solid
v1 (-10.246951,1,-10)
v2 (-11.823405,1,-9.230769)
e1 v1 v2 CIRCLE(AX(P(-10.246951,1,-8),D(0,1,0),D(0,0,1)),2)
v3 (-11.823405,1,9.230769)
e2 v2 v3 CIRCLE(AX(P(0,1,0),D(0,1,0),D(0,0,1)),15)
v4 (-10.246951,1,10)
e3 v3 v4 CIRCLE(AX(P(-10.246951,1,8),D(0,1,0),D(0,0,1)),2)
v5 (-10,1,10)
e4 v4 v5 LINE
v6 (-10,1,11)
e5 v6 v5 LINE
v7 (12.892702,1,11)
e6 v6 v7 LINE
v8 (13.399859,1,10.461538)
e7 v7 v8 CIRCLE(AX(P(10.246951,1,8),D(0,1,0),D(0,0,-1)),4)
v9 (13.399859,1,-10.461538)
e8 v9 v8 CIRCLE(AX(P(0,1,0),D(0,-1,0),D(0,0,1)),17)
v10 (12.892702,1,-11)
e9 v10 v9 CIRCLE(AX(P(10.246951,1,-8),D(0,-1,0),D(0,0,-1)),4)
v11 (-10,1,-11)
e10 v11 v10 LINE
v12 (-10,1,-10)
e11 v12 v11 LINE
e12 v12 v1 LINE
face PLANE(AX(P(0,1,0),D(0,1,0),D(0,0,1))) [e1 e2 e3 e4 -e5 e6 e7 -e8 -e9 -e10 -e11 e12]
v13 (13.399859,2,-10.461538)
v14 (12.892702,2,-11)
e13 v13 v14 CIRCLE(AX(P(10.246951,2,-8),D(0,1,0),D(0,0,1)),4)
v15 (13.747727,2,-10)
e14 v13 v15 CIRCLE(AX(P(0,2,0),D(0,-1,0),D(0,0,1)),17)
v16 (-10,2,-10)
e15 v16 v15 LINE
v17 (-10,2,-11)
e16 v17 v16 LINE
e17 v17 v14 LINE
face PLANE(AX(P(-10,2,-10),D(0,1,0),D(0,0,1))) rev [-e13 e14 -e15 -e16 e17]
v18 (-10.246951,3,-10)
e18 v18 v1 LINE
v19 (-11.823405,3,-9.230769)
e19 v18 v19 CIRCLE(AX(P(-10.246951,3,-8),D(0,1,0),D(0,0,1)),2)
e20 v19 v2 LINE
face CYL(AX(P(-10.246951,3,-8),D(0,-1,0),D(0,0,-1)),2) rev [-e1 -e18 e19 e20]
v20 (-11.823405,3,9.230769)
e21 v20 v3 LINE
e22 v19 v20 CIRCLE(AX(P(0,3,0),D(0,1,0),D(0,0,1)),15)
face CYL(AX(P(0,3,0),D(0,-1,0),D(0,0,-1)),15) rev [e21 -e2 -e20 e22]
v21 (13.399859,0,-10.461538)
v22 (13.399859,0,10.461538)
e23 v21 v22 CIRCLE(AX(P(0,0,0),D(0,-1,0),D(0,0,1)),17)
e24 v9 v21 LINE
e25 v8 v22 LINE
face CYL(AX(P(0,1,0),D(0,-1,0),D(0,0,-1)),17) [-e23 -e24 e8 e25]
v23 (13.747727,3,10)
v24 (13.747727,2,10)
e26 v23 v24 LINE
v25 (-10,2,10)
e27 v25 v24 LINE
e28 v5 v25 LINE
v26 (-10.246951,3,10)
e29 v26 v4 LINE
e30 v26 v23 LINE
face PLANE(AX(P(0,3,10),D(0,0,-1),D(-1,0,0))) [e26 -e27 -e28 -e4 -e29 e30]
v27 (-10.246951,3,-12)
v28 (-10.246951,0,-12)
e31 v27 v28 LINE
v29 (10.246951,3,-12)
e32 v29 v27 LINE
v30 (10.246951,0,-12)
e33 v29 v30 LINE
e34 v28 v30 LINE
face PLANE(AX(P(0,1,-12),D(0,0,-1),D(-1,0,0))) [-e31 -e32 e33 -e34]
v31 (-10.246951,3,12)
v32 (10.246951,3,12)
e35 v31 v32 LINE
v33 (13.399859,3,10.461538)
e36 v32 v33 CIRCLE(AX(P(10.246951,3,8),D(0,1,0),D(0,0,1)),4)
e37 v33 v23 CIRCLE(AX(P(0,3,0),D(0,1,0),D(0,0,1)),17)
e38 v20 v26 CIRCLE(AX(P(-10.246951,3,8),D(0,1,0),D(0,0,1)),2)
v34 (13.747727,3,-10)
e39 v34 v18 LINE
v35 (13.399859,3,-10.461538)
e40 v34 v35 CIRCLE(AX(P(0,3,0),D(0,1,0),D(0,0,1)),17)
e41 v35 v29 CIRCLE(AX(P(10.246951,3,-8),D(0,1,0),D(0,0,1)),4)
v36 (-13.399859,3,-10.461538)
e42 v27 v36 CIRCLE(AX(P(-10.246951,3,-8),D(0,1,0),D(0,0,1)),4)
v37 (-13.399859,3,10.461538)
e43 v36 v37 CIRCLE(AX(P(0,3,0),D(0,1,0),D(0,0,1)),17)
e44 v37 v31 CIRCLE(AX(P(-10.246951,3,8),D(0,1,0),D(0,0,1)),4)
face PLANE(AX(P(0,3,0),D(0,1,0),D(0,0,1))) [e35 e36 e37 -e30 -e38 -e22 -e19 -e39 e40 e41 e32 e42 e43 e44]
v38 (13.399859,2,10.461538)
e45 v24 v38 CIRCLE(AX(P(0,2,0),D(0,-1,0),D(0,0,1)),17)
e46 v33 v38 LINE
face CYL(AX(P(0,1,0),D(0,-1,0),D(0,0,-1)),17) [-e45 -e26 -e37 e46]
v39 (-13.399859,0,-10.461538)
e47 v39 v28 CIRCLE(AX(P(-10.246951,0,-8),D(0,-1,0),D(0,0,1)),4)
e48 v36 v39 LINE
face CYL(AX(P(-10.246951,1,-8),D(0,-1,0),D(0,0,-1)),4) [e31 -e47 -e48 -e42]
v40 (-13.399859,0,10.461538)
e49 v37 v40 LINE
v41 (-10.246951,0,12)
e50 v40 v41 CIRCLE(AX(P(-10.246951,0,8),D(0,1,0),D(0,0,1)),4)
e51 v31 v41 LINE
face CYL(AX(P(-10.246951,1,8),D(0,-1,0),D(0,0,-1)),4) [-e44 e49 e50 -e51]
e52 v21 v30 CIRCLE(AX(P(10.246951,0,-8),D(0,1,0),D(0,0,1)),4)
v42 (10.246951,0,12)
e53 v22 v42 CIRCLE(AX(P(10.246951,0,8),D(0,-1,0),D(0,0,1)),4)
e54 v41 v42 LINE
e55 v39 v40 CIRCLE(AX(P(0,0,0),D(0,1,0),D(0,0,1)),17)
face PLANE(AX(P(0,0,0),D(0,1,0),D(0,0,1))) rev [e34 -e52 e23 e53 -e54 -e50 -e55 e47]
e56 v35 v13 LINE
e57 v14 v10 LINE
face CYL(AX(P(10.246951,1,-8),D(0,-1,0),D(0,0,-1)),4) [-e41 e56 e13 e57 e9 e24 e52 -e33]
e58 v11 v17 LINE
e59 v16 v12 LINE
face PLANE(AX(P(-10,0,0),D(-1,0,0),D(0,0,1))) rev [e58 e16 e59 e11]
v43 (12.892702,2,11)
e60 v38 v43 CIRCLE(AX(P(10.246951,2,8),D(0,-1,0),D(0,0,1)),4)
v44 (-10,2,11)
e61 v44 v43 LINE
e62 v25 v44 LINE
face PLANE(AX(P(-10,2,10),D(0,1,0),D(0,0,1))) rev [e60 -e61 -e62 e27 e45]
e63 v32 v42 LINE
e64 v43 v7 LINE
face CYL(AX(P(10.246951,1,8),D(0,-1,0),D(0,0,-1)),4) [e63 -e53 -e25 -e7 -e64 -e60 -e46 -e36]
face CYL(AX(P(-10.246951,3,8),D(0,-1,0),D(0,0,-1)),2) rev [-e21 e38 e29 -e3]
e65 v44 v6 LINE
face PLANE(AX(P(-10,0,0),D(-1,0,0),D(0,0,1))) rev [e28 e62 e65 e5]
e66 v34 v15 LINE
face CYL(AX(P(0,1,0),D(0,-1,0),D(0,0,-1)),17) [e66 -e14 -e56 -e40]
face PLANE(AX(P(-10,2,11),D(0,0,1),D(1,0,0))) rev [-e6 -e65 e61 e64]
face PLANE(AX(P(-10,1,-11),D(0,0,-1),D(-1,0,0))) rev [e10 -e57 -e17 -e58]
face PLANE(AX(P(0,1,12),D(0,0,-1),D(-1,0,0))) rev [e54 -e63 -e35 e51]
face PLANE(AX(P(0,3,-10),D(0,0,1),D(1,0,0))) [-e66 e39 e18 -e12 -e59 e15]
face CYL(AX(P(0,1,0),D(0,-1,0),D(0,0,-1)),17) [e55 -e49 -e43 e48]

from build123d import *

# Parameters (mm, degrees)
BASE_PLATE_DEPTH       = 1
RIM_WALL_DEPTH         = 2
SIDE_GROOVE_A_SKETCH_W = 1
SIDE_GROOVE_A_SKETCH_H = 1
SIDE_GROOVE_A_DEPTH    = 40
SIDE_GROOVE_B_SKETCH_W = 1
SIDE_GROOVE_B_SKETCH_H = 1
SIDE_GROOVE_B_DEPTH    = 40


with BuildPart() as part:
    # Base Plate Sketch → Base Plate (new body)
    with BuildSketch(Plane(origin=(0, 0, 0), x_dir=(1, 0, 0), z_dir=(0, 1, 0))):
        with BuildLine():
            Line((-10.246950766, 12), (10.246950766, 12))
            ThreePointArc((10.246950766, 12), (12.001066805, 11.594868137), (13.399858694, 10.461538462))
            ThreePointArc((13.399858694, 10.461538462), (17, 0), (13.399858694, -10.461538462))
            ThreePointArc((13.399858694, -10.461538462), (12.001066805, -11.594868137), (10.246950766, -12))
            Line((10.246950766, -12), (-10.246950766, -12))
            ThreePointArc((-10.246950766, -12), (-12.001066805, -11.594868137), (-13.399858694, -10.461538462))
            ThreePointArc((-13.399858694, -10.461538462), (-17, 0), (-13.399858694, 10.461538462))
            ThreePointArc((-13.399858694, 10.461538462), (-12.001066805, 11.594868137), (-10.246950766, 12))
        make_face()
    extrude(amount=BASE_PLATE_DEPTH)

    # Rim Wall Sketch → Rim Wall (add)
    with BuildSketch(Plane(origin=(0, 1, 0), x_dir=(1, 0, 0), z_dir=(0, 1, 0))):
        with BuildLine():
            Line((10.246950766, -10), (-10.246950766, -10))
            ThreePointArc((-10.246950766, -10), (-11.124008785, -9.797434069), (-11.82340473, -9.230769231))
            ThreePointArc((-11.82340473, -9.230769231), (-15, 0), (-11.82340473, 9.230769231))
            ThreePointArc((-11.82340473, 9.230769231), (-11.124008785, 9.797434069), (-10.246950766, 10))
            Line((-10.246950766, 10), (10.246950766, 10))
            Line((10.246950766, 10), (13.747727085, 10))
            ThreePointArc((13.747727085, 10), (13.575754412, 10.232247659), (13.399858694, 10.461538462))
            ThreePointArc((13.399858694, 10.461538462), (12.001066805, 11.594868137), (10.246950766, 12))
            Line((10.246950766, 12), (-10.246950766, 12))
            ThreePointArc((-10.246950766, 12), (-12.001066805, 11.594868137), (-13.399858694, 10.461538462))
            ThreePointArc((-13.399858694, 10.461538462), (-17, 0), (-13.399858694, -10.461538462))
            ThreePointArc((-13.399858694, -10.461538462), (-12.001066805, -11.594868137), (-10.246950766, -12))
            Line((-10.246950766, -12), (10.246950766, -12))
            ThreePointArc((10.246950766, -12), (12.001066805, -11.594868137), (13.399858694, -10.461538462))
            ThreePointArc((13.399858694, -10.461538462), (13.575754412, -10.232247659), (13.747727085, -10))
            Line((13.747727085, -10), (10.246950766, -10))
        make_face()
    extrude(amount=RIM_WALL_DEPTH)

    # Side Groove A Sketch → Side Groove A (cut)
    with BuildSketch(Plane(origin=(30, 0, 0), x_dir=(0, 0, -1), z_dir=(1, 0, 0))):
        with Locations((-10.5, 1.5)):
            Rectangle(SIDE_GROOVE_A_SKETCH_W, SIDE_GROOVE_A_SKETCH_H)
    extrude(amount=-SIDE_GROOVE_A_DEPTH, mode=Mode.SUBTRACT)

    # Side Groove B Sketch → Side Groove B (cut)
    with BuildSketch(Plane(origin=(30, 0, 0), x_dir=(0, 0, -1), z_dir=(1, 0, 0))):
        with Locations((10.5, 1.5)):
            Rectangle(SIDE_GROOVE_B_SKETCH_W, SIDE_GROOVE_B_SKETCH_H)
    extrude(amount=-SIDE_GROOVE_B_DEPTH, mode=Mode.SUBTRACT)


solid = part.part
